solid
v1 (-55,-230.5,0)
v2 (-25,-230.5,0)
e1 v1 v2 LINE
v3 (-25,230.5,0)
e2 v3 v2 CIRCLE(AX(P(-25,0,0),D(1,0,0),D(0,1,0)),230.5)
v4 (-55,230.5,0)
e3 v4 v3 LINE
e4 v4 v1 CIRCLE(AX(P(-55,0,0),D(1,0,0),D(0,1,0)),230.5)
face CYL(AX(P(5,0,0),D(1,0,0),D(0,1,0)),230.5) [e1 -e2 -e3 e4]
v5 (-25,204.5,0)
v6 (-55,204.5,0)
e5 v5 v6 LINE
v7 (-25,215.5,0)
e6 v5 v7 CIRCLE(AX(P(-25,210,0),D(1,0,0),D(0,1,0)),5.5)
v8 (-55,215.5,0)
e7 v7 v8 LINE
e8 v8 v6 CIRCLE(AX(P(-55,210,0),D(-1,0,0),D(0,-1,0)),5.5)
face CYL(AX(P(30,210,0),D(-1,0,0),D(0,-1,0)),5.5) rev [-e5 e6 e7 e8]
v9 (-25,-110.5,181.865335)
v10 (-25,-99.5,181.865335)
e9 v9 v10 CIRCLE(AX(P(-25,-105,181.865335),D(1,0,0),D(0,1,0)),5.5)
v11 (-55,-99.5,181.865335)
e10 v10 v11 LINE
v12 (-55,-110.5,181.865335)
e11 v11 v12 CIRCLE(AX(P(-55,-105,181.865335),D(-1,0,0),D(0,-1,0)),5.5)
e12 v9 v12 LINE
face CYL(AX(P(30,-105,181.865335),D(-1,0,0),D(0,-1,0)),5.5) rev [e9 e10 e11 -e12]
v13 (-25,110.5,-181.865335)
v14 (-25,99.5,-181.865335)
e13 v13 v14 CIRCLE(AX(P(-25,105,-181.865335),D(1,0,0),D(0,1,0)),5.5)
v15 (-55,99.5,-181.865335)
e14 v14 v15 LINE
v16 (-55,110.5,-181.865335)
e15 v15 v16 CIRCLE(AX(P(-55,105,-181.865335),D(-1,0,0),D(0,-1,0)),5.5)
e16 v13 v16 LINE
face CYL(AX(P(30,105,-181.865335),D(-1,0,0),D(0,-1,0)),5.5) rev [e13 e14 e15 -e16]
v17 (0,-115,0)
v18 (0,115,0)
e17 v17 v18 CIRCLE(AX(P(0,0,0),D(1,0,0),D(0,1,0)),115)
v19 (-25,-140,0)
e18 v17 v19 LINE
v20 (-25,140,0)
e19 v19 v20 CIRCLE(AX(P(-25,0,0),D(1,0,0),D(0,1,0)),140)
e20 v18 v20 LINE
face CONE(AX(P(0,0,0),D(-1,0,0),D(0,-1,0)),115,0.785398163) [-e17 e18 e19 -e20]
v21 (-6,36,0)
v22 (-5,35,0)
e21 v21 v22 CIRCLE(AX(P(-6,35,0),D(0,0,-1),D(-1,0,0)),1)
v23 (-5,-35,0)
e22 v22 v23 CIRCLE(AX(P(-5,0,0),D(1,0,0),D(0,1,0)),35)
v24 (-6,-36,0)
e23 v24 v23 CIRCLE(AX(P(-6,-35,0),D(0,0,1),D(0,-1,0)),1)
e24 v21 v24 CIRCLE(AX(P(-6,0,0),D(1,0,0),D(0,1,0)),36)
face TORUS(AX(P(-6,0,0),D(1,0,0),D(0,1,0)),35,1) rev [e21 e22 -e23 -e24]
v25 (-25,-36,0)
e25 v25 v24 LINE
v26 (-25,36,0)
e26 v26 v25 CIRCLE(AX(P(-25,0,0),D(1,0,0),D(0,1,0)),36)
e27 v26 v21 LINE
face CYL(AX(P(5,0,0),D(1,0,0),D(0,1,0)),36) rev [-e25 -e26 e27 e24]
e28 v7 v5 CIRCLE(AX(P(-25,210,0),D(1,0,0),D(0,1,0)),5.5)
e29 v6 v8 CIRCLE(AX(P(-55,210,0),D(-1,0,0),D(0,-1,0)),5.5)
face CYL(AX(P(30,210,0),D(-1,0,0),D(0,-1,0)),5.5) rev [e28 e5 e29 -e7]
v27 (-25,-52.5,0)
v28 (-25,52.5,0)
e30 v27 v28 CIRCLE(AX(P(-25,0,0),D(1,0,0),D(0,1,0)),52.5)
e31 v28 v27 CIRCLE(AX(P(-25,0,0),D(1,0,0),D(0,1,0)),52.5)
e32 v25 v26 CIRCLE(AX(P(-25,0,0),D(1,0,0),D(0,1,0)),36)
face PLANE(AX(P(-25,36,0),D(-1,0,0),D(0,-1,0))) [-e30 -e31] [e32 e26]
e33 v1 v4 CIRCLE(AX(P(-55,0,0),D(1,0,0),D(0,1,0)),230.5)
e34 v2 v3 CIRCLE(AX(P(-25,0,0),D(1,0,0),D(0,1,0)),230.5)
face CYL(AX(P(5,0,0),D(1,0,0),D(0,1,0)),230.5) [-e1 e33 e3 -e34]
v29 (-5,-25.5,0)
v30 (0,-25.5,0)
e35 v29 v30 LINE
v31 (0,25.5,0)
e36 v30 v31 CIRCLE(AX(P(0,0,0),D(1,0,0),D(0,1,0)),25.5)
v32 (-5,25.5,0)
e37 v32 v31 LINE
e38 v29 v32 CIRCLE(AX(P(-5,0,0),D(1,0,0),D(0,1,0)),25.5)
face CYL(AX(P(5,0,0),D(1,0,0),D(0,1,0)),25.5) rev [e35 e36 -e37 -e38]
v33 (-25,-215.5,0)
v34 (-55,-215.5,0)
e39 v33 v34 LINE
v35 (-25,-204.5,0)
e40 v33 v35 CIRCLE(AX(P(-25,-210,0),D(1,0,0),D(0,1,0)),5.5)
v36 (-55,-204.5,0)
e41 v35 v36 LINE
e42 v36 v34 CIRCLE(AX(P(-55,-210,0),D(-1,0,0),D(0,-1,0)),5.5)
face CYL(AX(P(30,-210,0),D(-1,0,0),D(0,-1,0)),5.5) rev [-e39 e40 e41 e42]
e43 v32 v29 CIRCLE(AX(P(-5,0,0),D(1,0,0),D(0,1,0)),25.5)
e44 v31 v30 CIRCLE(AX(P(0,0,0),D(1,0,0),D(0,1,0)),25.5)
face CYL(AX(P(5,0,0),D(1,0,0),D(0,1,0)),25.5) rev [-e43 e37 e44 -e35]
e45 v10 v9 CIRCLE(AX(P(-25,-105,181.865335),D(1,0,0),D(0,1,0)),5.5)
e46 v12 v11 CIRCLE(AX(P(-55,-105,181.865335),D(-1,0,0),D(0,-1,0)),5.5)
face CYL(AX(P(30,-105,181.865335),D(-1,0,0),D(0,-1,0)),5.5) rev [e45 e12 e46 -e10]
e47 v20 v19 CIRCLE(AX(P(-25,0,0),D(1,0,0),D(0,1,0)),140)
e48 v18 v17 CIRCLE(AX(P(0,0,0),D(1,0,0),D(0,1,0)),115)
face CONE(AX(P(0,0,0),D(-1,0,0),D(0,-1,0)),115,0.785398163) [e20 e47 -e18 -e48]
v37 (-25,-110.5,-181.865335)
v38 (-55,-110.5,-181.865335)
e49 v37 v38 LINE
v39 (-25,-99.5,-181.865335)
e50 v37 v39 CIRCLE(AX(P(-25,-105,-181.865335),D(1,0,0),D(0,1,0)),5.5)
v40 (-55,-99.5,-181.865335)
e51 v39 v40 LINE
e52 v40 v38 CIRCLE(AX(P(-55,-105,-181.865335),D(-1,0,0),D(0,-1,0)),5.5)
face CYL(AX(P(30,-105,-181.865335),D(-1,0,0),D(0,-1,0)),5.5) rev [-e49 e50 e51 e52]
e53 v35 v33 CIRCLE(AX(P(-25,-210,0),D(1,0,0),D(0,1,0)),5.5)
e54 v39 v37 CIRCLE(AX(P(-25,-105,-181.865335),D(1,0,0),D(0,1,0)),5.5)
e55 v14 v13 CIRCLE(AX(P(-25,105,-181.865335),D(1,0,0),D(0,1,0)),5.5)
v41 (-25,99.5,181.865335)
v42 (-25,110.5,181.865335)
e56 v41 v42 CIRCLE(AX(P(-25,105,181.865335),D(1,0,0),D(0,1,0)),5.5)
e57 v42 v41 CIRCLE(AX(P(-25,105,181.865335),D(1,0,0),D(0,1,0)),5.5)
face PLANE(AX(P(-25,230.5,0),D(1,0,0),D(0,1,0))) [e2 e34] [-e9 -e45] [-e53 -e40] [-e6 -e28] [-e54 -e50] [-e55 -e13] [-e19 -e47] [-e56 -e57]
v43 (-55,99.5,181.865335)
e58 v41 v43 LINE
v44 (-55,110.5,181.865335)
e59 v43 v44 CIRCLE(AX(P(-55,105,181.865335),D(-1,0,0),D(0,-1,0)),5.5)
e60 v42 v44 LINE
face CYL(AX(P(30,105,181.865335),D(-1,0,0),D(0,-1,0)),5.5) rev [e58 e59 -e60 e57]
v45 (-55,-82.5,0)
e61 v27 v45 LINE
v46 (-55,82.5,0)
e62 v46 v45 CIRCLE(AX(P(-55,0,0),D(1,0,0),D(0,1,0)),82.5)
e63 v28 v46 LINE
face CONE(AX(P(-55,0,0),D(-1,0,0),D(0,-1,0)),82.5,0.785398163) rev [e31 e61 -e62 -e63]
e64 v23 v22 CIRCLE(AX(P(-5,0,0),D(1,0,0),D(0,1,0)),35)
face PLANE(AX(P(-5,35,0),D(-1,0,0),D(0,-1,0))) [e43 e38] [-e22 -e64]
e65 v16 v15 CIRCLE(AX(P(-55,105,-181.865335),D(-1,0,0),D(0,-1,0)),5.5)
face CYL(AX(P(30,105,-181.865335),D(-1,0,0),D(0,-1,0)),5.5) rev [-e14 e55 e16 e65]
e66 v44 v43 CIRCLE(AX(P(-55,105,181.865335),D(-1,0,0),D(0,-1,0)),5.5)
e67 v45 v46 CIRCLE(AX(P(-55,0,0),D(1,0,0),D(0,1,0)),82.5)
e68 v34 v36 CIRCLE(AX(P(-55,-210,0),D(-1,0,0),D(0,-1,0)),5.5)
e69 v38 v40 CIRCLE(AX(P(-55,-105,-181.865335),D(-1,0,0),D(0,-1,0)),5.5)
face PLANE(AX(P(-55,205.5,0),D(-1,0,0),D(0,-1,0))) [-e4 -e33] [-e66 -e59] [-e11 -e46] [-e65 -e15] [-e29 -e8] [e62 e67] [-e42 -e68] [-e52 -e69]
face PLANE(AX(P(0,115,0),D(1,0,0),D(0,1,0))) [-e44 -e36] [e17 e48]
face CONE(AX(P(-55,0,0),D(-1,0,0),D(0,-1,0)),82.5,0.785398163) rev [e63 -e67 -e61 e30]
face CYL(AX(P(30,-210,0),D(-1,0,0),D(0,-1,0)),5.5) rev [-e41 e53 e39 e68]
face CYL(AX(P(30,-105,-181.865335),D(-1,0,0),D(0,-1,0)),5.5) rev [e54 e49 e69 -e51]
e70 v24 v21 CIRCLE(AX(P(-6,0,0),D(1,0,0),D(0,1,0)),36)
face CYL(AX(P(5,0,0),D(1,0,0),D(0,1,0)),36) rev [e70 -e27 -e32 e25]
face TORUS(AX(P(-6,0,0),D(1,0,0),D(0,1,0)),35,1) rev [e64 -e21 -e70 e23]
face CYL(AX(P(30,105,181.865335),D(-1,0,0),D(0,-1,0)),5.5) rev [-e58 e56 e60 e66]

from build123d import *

# Parameters (mm, degrees)
SKETCH2_R          = 5.5
CUT_EXTRUDE1_DEPTH = 85


with BuildPart() as part:
    # Sketch1 → Revolve1 (revolve)
    with BuildSketch(Plane.XY):
        with BuildLine():
            Line((-25, 230.5), (-25, 140))
            Line((-25, 140), (0, 115))
            Line((0, 115), (0, 25.5))
            Line((0, 25.5), (-5, 25.5))
            Line((-5, 25.5), (-5, 35))
            ThreePointArc((-5, 35), (-5.292893219, 35.707106781), (-6, 36))
            Line((-6, 36), (-25, 36))
            Line((-25, 36), (-25, 52.5))
            Line((-25, 52.5), (-55, 82.5))
            Line((-55, 82.5), (-55, 205.5))
            Line((-55, 205.5), (-55, 215.5))
            Line((-55, 215.5), (-55, 230.5))
            Line((-55, 230.5), (-25, 230.5))
        make_face()
    revolve(axis=Axis((5, 0, 0), (-1, 0, 0)))

    # Sketch2 → Cut-Extrude1 (cut)
    with BuildSketch(Plane.ZY.offset(55)):
        with Locations(Location((0, 210, 0), (0, 0, 270))):
            Circle(SKETCH2_R)
        with Locations(Location((181.865334795, 105, 0), (0, 0, 270))):
            Circle(SKETCH2_R)
        with Locations(Location((181.865334795, -105, 0), (0, 0, 270))):
            Circle(SKETCH2_R)
        with Locations(Location((0, -210, 0), (0, 0, 270))):
            Circle(SKETCH2_R)
        with Locations(Location((-181.865334795, -105, 0), (0, 0, 270))):
            Circle(SKETCH2_R)
        with Locations(Location((-181.865334795, 105, 0), (0, 0, 270))):
            Circle(SKETCH2_R)
    extrude(amount=-CUT_EXTRUDE1_DEPTH, mode=Mode.SUBTRACT)


solid = part.part
